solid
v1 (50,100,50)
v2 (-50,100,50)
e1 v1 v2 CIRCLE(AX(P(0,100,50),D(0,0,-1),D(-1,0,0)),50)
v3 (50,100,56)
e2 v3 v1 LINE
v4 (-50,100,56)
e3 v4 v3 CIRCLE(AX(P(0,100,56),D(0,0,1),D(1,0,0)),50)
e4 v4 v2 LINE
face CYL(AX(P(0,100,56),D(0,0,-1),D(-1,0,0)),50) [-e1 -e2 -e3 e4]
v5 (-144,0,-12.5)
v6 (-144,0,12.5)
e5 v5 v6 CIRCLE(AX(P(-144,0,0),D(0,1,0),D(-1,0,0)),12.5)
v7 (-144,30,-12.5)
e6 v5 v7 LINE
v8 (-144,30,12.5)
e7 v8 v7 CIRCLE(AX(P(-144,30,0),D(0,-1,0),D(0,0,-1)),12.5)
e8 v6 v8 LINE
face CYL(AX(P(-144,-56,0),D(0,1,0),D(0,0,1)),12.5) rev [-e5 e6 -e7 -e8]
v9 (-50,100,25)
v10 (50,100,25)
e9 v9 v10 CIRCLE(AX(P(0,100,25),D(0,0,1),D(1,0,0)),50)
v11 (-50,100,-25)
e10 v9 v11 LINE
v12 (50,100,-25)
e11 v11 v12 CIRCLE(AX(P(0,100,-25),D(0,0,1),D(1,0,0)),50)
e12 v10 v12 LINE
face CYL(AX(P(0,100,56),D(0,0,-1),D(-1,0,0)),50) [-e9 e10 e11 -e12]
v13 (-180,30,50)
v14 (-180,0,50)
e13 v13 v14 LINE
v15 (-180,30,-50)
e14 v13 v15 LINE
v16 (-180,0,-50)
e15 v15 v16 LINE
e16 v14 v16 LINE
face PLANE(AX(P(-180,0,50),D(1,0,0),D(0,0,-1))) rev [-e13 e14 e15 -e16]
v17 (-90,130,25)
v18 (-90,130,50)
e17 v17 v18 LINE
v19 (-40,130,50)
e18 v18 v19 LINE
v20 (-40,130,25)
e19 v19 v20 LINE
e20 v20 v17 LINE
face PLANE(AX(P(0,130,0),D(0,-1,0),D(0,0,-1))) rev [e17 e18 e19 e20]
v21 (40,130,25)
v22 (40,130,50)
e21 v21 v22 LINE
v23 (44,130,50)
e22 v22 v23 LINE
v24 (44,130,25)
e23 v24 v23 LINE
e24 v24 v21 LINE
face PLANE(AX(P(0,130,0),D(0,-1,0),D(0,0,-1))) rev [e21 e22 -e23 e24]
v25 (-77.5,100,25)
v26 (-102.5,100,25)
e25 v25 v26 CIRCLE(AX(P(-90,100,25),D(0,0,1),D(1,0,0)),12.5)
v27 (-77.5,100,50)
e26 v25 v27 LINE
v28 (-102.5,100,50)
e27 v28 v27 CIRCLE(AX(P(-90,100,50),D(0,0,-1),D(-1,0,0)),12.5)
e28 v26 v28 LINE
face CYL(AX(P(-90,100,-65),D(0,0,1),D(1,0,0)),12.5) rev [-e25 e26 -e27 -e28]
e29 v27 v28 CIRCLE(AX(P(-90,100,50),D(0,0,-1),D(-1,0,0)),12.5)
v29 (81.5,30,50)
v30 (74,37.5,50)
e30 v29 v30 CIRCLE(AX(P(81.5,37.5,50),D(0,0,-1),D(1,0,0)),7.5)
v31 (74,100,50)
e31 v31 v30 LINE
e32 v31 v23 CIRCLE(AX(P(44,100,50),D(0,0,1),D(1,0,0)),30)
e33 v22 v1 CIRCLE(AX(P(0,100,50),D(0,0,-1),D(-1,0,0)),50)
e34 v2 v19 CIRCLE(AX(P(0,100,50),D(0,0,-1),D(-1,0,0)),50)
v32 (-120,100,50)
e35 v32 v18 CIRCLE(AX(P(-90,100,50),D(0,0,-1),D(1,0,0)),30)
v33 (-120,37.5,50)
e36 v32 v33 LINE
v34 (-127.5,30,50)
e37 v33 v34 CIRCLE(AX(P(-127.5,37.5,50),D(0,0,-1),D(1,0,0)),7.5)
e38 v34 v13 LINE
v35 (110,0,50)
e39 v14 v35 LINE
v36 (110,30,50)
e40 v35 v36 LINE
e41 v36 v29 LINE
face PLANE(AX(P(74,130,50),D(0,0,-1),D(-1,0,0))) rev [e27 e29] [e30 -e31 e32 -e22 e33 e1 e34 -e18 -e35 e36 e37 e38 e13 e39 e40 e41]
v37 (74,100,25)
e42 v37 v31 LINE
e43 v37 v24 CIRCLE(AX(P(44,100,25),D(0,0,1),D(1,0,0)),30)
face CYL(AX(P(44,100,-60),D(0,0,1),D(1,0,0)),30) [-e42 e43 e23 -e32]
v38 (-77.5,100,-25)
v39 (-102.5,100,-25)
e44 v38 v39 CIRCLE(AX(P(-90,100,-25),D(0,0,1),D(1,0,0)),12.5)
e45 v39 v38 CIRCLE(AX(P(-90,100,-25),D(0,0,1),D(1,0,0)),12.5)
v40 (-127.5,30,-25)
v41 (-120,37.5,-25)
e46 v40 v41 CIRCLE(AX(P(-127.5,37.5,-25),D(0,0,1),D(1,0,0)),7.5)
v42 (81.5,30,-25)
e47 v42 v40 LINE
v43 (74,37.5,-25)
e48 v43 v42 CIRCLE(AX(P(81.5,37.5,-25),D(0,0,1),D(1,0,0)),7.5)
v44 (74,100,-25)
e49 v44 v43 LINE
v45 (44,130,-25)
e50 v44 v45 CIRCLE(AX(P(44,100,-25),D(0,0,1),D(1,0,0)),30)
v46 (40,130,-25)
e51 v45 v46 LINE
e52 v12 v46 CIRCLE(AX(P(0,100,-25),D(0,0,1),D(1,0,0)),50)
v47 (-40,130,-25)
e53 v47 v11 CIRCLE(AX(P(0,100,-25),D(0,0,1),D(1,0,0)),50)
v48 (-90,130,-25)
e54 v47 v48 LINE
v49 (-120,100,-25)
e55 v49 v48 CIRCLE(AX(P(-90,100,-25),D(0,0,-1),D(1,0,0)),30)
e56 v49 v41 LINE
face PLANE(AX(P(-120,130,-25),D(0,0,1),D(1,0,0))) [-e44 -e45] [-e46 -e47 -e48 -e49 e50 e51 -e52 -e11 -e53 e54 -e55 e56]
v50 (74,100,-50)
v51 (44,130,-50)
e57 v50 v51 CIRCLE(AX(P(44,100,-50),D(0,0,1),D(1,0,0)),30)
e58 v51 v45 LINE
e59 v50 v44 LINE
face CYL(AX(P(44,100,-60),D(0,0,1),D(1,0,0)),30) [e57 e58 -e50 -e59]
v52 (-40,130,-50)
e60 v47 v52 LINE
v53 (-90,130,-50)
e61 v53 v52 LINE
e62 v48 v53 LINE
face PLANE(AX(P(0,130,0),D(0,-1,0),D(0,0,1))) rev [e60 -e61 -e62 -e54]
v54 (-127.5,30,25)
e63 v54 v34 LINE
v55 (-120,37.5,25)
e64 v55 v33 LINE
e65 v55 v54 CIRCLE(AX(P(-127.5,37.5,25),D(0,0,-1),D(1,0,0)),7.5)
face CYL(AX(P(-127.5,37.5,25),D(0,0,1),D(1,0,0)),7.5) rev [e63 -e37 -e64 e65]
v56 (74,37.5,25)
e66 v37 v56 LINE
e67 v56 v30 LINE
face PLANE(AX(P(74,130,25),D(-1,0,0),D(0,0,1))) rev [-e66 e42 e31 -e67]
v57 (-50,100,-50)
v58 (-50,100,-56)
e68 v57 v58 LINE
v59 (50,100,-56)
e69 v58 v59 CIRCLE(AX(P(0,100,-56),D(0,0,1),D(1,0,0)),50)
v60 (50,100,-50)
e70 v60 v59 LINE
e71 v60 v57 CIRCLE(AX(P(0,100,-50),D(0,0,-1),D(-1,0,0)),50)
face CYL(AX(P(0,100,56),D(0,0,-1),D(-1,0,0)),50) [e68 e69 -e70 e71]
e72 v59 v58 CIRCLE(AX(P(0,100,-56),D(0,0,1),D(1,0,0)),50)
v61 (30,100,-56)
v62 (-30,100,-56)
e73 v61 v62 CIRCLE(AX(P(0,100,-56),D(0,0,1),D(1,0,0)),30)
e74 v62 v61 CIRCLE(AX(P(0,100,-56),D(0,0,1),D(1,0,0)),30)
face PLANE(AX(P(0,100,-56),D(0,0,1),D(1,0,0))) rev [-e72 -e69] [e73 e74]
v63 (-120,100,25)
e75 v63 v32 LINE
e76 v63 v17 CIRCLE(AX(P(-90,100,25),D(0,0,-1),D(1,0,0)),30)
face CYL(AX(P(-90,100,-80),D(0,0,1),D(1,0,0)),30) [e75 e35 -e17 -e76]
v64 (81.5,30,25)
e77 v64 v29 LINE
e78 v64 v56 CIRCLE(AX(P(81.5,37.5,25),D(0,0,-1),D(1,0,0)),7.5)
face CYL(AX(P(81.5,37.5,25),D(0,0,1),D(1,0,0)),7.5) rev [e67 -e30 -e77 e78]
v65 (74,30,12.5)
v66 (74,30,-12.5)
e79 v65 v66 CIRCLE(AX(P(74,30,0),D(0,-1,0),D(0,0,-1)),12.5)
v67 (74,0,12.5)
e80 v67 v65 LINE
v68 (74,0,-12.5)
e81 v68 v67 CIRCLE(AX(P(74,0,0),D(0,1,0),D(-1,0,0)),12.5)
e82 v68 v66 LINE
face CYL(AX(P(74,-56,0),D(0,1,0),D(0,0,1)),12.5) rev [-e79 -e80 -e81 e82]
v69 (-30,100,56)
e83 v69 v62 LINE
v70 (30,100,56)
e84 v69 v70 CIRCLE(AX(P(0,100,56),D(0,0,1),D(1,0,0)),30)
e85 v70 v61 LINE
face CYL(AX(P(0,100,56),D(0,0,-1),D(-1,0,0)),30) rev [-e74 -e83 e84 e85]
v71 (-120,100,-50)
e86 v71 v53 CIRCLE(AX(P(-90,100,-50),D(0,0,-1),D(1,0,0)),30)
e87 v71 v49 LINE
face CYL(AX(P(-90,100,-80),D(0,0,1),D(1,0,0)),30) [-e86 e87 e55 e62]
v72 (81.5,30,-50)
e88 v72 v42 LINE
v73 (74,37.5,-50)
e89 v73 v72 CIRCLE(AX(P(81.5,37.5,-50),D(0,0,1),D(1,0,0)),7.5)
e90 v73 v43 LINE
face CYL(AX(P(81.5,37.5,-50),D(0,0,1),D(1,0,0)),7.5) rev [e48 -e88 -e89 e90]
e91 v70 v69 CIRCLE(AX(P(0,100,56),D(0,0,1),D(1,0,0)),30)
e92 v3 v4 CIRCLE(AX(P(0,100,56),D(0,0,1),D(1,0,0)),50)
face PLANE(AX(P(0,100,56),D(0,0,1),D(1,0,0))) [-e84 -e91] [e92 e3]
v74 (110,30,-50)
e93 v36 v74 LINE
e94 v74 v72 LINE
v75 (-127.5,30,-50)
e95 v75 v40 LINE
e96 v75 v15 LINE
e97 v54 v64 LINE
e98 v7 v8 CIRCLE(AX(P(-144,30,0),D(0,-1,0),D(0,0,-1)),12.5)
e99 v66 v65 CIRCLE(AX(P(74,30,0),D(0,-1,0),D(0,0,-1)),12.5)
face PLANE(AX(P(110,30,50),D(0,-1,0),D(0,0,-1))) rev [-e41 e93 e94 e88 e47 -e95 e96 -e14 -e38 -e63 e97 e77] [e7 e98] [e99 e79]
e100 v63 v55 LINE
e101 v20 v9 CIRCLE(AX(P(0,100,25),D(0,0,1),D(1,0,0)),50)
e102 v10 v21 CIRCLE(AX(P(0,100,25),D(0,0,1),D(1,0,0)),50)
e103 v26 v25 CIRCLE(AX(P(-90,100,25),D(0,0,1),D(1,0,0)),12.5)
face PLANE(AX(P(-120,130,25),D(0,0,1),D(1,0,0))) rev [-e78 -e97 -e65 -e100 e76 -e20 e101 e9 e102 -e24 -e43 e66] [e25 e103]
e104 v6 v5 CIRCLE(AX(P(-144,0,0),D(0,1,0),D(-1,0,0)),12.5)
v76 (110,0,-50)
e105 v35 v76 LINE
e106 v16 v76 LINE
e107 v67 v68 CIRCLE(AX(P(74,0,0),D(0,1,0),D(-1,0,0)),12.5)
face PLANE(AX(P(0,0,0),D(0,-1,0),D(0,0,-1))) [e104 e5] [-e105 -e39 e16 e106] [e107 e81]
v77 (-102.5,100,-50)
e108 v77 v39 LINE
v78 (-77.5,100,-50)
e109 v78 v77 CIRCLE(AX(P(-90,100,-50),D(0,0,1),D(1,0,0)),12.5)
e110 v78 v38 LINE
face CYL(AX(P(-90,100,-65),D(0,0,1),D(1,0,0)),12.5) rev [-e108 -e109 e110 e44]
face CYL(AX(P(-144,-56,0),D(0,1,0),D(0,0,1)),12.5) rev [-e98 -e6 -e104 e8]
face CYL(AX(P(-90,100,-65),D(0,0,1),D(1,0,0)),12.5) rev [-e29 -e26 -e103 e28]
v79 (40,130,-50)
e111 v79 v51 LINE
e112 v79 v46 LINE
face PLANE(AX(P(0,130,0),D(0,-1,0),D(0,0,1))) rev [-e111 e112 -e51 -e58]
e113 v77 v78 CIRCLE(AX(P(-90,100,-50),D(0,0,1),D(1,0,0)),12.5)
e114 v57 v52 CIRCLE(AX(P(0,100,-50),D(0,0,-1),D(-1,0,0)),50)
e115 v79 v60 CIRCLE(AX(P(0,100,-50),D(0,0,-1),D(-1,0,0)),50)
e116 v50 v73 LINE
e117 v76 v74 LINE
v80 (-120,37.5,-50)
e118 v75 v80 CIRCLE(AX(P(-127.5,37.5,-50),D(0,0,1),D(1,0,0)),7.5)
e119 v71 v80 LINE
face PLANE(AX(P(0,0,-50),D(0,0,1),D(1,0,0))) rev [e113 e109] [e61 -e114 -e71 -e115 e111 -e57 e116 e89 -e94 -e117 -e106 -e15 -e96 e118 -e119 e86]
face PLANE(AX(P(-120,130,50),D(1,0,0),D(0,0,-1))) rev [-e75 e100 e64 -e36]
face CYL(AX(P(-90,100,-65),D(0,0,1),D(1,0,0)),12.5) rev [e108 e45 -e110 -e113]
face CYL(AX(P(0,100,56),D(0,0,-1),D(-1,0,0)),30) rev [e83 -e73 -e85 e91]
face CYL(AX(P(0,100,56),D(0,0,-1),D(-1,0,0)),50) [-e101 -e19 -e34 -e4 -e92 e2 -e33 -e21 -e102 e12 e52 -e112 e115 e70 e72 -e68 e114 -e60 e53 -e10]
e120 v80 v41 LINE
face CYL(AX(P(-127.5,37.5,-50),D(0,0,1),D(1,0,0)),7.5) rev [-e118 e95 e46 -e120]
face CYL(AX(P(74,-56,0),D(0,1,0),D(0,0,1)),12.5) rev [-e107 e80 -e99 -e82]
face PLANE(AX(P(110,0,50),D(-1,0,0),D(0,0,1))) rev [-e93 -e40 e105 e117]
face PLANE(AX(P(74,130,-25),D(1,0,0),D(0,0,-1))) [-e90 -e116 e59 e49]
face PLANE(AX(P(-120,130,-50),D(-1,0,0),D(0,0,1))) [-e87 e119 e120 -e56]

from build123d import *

# Parameters (mm, degrees)
BASE_PLATE_SKETCH_W         = 290
BASE_PLATE_SKETCH_H         = 30
BASE_PLATE_DEPTH            = 50
BEARING_BOSS_SKETCH_R       = 50
BEARING_BOSS_SKETCH_R_2     = 30
BEARING_BOSS_DEPTH          = 56
BASE_MOUNTING_CUT_SKETCH_R  = 12.5
BASE_MOUNTING_CUT_DEPTH     = 56
SUPPORT_LUG_SKETCH_W        = 194
SUPPORT_LUG_SKETCH_H        = 25
SUPPORT_LUG_DEPTH           = 130
LUG_PIN_HOLE_SKETCH_R       = 12.5
LUG_PIN_HOLE_25_DEPTH       = 65
LUG_PROFILE_CUT_DEPTH       = 130
HOUSING_CLEARANCE_CUT_DEPTH = 110
BEARING_START               = -120
BEARING_BORE_SKETCH_R       = 30
BEARING_BORE_60_DEPTH       = 120
RIB_1_DEPTH                 = 25
RIB_2_DEPTH                 = 25
RIB_3_DEPTH                 = 25
RIB_4_DEPTH                 = 25


with BuildPart() as part:
    # Base Plate Sketch → Base Plate (new, symmetric)
    with BuildSketch(Plane.XY):
        with Locations((-35, 15)):
            Rectangle(BASE_PLATE_SKETCH_W, BASE_PLATE_SKETCH_H)
    extrude(amount=BASE_PLATE_DEPTH, both=True)

    # Base Mounting Cut Sketch → Base Mounting Cut (cut, symmetric)
    with BuildSketch(Plane(origin=(0, 0, 0), x_dir=(1, 0, 0), z_dir=(0, 1, 0))):
        with Locations(Location((-144, 0, 0), (0, 0, 180))):
            Circle(BASE_MOUNTING_CUT_SKETCH_R)
        with Locations(Location((74, 0, 0), (0, 0, 180))):
            Circle(BASE_MOUNTING_CUT_SKETCH_R)
    extrude(amount=BASE_MOUNTING_CUT_DEPTH, both=True, mode=Mode.SUBTRACT)



with BuildPart() as body_2:
    # Bearing Boss Sketch → Bearing Boss (new, symmetric)
    with BuildSketch(Plane.XY):
        with Locations((0, 100)):
            Circle(BEARING_BOSS_SKETCH_R)
        with Locations((0, 100)):
            Circle(BEARING_BOSS_SKETCH_R_2, mode=Mode.SUBTRACT)
    extrude(amount=BEARING_BOSS_DEPTH, both=True)


with BuildPart() as part_1:
    add(part.part)

    add(body_2.part)  # Support Lug merges body 2
    # Support Lug Sketch → Support Lug (add)
    with BuildSketch(Plane(origin=(0, 0, 0), x_dir=(1, 0, 0), z_dir=(0, 1, 0))):
        with Locations((-23, -37.5)):
            Rectangle(SUPPORT_LUG_SKETCH_W, SUPPORT_LUG_SKETCH_H)
    support_lug = extrude(amount=SUPPORT_LUG_DEPTH)

    # Support Lug Mirror: Support Lug across plane
    add(support_lug.mirror(Plane.XY))

    # Lug Pin Hole Sketch → Lug Pin Hole Ø25 (cut, symmetric)
    with BuildSketch(Plane.XY):
        with Locations((-90, 100)):
            Circle(LUG_PIN_HOLE_SKETCH_R)
    extrude(amount=LUG_PIN_HOLE_25_DEPTH, both=True, mode=Mode.SUBTRACT)

    # Lug Profile Cut Sketch → Lug Profile Cut (cut)
    with BuildSketch(Plane.XY.offset(50)):
        with BuildLine():
            Line((-120, 100), (-120, 130))
            Line((-120, 130), (-90, 130))
            ThreePointArc((-90, 130), (-111.213203436, 121.213203436), (-120, 100))
        make_face()
    extrude(amount=-LUG_PROFILE_CUT_DEPTH, mode=Mode.SUBTRACT)

    # Housing Clearance Sketch → Housing Clearance Cut (cut)
    with BuildSketch(Plane.XY.offset(50)):
        with BuildLine():
            Line((74, 130), (44, 130))
            ThreePointArc((44, 130), (65.213203436, 121.213203436), (74, 100))
            Line((74, 100), (74, 130))
        make_face()
    extrude(amount=-HOUSING_CLEARANCE_CUT_DEPTH, mode=Mode.SUBTRACT)

    # Bearing Bore Sketch → Bearing Bore Ø60 (cut)
    with BuildSketch(Plane.XY.offset(56).offset(BEARING_START)):
        with Locations((0, 100)):
            Circle(BEARING_BORE_SKETCH_R)
    extrude(amount=BEARING_BORE_60_DEPTH, mode=Mode.SUBTRACT)

    # Rib 1 Sketch → Rib 1 (add)
    with BuildSketch(Plane.XY.offset(50)):
        with BuildLine():
            Line((-127.5, 30), (-120, 30))
            Line((-120, 30), (-120, 37.5))
            ThreePointArc((-120, 37.5), (-122.196699141, 32.196699141), (-127.5, 30))
        make_face()
    extrude(amount=-RIB_1_DEPTH)

    # Rib 2 Sketch → Rib 2 (add)
    with BuildSketch(Plane.XY.offset(-25)):
        with BuildLine():
            Line((-127.5, 30), (-120, 30))
            Line((-120, 30), (-120, 37.5))
            ThreePointArc((-120, 37.5), (-122.196699141, 32.196699141), (-127.5, 30))
        make_face()
    extrude(amount=-RIB_2_DEPTH)

    # Rib 3 Sketch → Rib 3 (add)
    with BuildSketch(Plane.XY.offset(50)):
        with BuildLine():
            Line((74, 37.5), (74, 30))
            Line((74, 30), (81.5, 30))
            ThreePointArc((81.5, 30), (76.196699141, 32.196699141), (74, 37.5))
        make_face()
    extrude(amount=-RIB_3_DEPTH)

    # Rib 4 Sketch → Rib 4 (add)
    with BuildSketch(Plane.XY.offset(-25)):
        with BuildLine():
            Line((74, 30), (81.5, 30))
            ThreePointArc((81.5, 30), (76.196699141, 32.196699141), (74, 37.5))
            Line((74, 37.5), (74, 30))
        make_face()
    extrude(amount=-RIB_4_DEPTH)


solid = part_1.part
